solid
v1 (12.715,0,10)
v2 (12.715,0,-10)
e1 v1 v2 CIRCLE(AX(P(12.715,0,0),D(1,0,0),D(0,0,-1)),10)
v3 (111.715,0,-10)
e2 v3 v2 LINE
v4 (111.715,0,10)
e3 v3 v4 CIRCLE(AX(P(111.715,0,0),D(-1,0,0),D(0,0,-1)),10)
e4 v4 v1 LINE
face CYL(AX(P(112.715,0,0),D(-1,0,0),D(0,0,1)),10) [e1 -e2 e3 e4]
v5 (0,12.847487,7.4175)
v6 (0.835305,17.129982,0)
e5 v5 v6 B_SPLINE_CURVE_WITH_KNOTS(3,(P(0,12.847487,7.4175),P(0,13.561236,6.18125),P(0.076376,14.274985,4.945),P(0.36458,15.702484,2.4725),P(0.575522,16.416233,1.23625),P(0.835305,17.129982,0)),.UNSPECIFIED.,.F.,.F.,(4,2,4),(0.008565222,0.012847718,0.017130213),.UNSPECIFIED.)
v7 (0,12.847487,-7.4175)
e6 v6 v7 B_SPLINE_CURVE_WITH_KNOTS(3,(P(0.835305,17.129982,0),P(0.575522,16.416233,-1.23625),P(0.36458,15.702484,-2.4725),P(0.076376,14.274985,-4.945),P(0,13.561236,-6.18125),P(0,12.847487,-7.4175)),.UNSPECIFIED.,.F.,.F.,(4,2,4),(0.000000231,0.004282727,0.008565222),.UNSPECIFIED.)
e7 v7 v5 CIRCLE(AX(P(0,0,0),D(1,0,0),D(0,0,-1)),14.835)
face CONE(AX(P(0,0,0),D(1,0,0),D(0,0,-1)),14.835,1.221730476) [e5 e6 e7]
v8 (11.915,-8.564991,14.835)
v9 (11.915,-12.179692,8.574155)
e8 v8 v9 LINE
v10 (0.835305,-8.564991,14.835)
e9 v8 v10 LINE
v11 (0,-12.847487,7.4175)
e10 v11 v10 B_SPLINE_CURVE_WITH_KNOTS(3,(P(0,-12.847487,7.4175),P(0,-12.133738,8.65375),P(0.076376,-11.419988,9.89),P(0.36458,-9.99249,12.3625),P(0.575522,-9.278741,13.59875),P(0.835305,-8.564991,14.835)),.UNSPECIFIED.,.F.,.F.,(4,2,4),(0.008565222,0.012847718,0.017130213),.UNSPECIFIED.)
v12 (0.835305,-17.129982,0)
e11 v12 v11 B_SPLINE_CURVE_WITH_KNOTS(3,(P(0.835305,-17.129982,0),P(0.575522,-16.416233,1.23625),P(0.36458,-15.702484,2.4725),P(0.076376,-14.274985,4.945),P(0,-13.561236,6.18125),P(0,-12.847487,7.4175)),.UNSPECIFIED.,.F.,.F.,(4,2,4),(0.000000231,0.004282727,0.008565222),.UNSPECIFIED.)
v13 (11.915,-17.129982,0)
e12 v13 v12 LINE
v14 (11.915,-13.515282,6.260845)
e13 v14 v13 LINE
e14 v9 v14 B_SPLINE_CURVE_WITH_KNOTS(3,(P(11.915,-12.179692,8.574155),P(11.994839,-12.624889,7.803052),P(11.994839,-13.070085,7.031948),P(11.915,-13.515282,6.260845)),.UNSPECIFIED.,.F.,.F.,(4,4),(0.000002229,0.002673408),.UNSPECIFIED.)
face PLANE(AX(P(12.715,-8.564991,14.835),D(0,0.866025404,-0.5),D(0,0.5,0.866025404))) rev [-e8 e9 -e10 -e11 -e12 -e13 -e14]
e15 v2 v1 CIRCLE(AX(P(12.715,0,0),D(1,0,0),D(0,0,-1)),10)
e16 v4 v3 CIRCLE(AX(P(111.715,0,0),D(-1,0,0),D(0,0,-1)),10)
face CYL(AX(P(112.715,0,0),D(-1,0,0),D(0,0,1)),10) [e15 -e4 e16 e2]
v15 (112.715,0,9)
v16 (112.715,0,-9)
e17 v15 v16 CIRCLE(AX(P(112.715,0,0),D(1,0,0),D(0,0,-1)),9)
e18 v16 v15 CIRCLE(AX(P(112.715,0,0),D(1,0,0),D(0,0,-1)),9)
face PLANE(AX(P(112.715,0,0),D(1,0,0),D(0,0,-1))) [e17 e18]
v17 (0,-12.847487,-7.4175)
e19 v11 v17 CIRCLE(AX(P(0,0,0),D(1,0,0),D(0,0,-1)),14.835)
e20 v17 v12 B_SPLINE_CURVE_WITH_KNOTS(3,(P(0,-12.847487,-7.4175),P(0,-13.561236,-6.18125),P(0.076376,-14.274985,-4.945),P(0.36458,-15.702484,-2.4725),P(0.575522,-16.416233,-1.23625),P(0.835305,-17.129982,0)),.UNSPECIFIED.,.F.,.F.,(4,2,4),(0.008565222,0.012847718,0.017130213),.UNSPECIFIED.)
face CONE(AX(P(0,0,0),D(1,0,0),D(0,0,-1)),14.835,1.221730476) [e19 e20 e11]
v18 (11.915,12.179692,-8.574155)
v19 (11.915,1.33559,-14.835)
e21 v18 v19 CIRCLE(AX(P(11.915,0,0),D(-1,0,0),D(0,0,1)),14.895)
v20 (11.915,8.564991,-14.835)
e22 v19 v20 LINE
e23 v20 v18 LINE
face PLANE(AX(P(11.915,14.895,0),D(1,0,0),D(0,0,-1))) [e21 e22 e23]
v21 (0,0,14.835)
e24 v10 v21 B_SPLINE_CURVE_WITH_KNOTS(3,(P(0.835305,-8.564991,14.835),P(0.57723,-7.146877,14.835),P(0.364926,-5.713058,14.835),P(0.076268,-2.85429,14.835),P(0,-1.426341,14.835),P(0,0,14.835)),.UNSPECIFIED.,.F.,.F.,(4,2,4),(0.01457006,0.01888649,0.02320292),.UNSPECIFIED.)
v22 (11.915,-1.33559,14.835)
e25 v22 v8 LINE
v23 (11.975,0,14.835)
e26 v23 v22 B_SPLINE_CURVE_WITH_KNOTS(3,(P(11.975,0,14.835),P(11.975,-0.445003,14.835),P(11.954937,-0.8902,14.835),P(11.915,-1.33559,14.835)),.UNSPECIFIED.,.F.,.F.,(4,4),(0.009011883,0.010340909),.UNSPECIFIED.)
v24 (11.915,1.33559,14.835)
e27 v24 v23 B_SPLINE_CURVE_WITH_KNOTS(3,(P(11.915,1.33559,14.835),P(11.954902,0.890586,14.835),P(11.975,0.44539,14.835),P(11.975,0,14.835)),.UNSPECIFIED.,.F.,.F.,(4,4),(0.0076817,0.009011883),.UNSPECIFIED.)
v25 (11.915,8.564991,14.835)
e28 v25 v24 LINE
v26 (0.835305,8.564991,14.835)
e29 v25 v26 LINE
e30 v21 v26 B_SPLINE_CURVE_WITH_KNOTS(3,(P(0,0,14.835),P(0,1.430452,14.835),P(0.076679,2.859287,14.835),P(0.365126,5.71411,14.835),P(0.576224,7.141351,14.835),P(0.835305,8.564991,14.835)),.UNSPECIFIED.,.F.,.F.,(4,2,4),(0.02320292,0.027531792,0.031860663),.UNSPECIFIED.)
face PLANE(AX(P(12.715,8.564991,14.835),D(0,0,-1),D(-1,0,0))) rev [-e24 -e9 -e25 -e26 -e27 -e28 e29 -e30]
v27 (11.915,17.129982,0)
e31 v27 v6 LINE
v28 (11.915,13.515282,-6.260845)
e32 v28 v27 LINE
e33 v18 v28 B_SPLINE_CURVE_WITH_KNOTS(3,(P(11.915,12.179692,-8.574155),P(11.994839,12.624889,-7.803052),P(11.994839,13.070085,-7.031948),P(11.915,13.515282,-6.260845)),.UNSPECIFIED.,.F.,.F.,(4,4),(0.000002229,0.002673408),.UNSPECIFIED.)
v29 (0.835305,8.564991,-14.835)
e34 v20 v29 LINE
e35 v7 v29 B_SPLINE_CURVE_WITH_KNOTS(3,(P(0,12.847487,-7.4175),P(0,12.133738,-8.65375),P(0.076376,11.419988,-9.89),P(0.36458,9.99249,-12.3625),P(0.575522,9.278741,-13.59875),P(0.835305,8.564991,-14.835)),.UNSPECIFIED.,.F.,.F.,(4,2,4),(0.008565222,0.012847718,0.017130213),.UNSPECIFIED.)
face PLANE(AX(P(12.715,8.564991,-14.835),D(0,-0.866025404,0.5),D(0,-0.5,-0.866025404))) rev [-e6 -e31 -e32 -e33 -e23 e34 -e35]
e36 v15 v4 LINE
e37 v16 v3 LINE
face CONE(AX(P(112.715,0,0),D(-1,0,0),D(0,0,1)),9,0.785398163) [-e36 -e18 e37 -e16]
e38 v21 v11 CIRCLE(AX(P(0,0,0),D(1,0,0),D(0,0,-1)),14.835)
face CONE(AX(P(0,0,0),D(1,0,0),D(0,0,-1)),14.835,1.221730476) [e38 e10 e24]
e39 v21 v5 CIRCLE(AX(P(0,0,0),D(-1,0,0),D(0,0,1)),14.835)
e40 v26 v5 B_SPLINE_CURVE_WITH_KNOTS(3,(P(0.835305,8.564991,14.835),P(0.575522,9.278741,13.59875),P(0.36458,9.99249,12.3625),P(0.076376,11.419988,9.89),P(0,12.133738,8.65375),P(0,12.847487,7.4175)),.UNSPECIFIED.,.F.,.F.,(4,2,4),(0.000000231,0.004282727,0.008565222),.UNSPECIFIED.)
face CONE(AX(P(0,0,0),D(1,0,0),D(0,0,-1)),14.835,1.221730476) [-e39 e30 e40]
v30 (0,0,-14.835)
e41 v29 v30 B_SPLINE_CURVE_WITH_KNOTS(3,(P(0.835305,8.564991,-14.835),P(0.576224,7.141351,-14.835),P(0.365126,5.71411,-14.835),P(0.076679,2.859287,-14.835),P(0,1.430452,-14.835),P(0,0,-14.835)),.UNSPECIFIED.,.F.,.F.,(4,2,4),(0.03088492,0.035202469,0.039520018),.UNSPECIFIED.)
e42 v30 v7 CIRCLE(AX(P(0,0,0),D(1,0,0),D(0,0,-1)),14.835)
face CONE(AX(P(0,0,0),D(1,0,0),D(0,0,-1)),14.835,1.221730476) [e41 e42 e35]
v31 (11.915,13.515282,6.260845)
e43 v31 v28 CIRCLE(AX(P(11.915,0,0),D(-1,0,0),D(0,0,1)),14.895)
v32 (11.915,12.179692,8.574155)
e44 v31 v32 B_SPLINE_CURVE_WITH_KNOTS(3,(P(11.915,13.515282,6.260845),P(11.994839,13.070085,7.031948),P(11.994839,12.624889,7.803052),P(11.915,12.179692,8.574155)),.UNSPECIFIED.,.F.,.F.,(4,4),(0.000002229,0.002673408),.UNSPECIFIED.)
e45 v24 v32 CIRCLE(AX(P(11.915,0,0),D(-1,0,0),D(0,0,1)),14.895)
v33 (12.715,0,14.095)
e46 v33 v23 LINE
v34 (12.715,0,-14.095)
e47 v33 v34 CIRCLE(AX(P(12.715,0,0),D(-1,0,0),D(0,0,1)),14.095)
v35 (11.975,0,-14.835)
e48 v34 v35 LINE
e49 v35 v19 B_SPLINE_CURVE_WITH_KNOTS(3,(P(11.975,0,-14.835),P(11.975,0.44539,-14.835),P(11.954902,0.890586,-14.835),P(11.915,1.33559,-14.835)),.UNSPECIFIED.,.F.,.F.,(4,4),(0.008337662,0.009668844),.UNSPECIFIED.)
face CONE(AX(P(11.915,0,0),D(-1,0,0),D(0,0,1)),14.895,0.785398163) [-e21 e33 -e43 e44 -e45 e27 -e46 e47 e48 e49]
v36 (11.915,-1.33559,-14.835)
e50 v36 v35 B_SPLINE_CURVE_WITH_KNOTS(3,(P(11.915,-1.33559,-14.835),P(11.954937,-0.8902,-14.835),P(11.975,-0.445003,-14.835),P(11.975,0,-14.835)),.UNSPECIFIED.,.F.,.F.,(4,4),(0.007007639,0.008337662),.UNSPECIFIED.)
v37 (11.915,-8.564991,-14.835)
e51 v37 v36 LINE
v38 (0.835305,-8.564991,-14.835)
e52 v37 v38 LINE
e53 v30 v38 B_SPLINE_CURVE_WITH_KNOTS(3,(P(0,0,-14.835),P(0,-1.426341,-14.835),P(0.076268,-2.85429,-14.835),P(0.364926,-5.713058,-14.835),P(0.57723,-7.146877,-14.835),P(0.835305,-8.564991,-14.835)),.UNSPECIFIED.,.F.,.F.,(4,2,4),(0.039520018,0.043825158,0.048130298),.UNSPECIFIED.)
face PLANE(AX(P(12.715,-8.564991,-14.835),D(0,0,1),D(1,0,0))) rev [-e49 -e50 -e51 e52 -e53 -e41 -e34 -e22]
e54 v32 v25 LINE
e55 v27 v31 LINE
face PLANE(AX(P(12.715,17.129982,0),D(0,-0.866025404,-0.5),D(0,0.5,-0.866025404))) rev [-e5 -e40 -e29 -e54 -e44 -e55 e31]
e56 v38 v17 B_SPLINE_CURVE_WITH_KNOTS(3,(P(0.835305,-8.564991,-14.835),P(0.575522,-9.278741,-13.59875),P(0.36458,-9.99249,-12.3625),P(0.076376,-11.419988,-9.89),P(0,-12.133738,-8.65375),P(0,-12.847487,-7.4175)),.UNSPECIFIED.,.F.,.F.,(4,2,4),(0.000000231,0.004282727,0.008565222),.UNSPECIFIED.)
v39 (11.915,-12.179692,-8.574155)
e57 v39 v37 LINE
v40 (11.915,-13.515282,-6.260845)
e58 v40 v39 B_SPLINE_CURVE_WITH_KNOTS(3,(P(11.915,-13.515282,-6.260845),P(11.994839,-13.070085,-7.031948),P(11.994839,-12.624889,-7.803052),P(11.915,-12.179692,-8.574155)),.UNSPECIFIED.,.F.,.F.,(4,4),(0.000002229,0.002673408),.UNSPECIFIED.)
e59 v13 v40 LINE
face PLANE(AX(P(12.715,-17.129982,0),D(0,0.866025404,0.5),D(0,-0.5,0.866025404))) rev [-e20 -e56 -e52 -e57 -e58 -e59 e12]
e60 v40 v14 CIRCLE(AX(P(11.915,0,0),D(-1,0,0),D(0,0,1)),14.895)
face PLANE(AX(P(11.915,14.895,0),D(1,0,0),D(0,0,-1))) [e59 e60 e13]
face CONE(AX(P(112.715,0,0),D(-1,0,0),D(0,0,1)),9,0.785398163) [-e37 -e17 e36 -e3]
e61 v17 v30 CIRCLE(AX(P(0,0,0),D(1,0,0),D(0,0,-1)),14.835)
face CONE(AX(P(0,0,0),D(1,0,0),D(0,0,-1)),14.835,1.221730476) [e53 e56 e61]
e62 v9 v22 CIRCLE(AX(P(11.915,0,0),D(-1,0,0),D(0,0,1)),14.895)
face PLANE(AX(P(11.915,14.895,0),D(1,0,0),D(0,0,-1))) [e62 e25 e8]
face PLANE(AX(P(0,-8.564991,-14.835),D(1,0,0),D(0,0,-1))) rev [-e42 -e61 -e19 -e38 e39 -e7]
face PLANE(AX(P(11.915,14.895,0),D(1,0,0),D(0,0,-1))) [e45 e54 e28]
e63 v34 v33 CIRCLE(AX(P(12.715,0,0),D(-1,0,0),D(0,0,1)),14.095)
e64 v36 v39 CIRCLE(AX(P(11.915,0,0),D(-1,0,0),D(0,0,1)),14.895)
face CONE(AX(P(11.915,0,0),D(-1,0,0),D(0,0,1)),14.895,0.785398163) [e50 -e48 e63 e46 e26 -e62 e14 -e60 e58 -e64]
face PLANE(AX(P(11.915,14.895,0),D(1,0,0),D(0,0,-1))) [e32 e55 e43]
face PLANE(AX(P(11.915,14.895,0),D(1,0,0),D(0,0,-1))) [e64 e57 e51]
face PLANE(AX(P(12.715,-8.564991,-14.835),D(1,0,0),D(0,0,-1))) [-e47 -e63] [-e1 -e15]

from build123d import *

# Parameters (mm, degrees)
BASEHEAD_DEPTH = 12.715
SKETCH5_R      = 10
BASEBODY_DEPTH = 100
CHAMFER1_SIZE  = 1


with BuildPart() as part:
    # Sketch2 → BaseHead (new body)
    with BuildSketch(Plane(origin=(0, 0, 0), x_dir=(0, 0, -1), z_dir=(1, 0, 0))):
        Polygon((14.835, -8.564991243), (14.835, 8.564991243), (0, 17.129982487), (-14.835, 8.564991243), (-14.835, -8.564991243), (0, -17.129982487), align=None)
    extrude(amount=BASEHEAD_DEPTH)

    # Sketch3 → BearingFace (revolve, cut)
    with BuildSketch(Plane.XY, mode=Mode.PRIVATE) as bearingface_sk:
        Polygon((12.715, 17.129982487), (12.715, 14.095), (11.915, 14.895), (11.915, 17.129982487), align=None)
    revolve(bearingface_sk.sketch.rotate(Axis((-0.957090588, 0, 0), (1, 0, 0)), 90), axis=Axis((-0.957090588, 0, 0), (1, 0, 0)), mode=Mode.SUBTRACT)

    # Sketch4 → HeadChamfer (revolve, cut)
    with BuildSketch(Plane.XY):
        Polygon((0, 17.129982487), (0.835305313, 17.129982487), (0, 14.835), align=None)
    revolve(axis=Axis((-0.493528746, 0, 0), (1, 0, 0)), mode=Mode.SUBTRACT)

    # Sketch5 → BaseBody (add)
    with BuildSketch(Plane(origin=(12.715, 0, 0), x_dir=(0, 0, -1), z_dir=(1, 0, 0))):
        Circle(SKETCH5_R)
    extrude(amount=BASEBODY_DEPTH)

    # Chamfer1
    chamfer1_edges = [part.edges().sort_by_distance(p)[0] for p in [
        (112.715, 0, 10),
    ]]
    chamfer(chamfer1_edges, length=CHAMFER1_SIZE)


solid = part.part
